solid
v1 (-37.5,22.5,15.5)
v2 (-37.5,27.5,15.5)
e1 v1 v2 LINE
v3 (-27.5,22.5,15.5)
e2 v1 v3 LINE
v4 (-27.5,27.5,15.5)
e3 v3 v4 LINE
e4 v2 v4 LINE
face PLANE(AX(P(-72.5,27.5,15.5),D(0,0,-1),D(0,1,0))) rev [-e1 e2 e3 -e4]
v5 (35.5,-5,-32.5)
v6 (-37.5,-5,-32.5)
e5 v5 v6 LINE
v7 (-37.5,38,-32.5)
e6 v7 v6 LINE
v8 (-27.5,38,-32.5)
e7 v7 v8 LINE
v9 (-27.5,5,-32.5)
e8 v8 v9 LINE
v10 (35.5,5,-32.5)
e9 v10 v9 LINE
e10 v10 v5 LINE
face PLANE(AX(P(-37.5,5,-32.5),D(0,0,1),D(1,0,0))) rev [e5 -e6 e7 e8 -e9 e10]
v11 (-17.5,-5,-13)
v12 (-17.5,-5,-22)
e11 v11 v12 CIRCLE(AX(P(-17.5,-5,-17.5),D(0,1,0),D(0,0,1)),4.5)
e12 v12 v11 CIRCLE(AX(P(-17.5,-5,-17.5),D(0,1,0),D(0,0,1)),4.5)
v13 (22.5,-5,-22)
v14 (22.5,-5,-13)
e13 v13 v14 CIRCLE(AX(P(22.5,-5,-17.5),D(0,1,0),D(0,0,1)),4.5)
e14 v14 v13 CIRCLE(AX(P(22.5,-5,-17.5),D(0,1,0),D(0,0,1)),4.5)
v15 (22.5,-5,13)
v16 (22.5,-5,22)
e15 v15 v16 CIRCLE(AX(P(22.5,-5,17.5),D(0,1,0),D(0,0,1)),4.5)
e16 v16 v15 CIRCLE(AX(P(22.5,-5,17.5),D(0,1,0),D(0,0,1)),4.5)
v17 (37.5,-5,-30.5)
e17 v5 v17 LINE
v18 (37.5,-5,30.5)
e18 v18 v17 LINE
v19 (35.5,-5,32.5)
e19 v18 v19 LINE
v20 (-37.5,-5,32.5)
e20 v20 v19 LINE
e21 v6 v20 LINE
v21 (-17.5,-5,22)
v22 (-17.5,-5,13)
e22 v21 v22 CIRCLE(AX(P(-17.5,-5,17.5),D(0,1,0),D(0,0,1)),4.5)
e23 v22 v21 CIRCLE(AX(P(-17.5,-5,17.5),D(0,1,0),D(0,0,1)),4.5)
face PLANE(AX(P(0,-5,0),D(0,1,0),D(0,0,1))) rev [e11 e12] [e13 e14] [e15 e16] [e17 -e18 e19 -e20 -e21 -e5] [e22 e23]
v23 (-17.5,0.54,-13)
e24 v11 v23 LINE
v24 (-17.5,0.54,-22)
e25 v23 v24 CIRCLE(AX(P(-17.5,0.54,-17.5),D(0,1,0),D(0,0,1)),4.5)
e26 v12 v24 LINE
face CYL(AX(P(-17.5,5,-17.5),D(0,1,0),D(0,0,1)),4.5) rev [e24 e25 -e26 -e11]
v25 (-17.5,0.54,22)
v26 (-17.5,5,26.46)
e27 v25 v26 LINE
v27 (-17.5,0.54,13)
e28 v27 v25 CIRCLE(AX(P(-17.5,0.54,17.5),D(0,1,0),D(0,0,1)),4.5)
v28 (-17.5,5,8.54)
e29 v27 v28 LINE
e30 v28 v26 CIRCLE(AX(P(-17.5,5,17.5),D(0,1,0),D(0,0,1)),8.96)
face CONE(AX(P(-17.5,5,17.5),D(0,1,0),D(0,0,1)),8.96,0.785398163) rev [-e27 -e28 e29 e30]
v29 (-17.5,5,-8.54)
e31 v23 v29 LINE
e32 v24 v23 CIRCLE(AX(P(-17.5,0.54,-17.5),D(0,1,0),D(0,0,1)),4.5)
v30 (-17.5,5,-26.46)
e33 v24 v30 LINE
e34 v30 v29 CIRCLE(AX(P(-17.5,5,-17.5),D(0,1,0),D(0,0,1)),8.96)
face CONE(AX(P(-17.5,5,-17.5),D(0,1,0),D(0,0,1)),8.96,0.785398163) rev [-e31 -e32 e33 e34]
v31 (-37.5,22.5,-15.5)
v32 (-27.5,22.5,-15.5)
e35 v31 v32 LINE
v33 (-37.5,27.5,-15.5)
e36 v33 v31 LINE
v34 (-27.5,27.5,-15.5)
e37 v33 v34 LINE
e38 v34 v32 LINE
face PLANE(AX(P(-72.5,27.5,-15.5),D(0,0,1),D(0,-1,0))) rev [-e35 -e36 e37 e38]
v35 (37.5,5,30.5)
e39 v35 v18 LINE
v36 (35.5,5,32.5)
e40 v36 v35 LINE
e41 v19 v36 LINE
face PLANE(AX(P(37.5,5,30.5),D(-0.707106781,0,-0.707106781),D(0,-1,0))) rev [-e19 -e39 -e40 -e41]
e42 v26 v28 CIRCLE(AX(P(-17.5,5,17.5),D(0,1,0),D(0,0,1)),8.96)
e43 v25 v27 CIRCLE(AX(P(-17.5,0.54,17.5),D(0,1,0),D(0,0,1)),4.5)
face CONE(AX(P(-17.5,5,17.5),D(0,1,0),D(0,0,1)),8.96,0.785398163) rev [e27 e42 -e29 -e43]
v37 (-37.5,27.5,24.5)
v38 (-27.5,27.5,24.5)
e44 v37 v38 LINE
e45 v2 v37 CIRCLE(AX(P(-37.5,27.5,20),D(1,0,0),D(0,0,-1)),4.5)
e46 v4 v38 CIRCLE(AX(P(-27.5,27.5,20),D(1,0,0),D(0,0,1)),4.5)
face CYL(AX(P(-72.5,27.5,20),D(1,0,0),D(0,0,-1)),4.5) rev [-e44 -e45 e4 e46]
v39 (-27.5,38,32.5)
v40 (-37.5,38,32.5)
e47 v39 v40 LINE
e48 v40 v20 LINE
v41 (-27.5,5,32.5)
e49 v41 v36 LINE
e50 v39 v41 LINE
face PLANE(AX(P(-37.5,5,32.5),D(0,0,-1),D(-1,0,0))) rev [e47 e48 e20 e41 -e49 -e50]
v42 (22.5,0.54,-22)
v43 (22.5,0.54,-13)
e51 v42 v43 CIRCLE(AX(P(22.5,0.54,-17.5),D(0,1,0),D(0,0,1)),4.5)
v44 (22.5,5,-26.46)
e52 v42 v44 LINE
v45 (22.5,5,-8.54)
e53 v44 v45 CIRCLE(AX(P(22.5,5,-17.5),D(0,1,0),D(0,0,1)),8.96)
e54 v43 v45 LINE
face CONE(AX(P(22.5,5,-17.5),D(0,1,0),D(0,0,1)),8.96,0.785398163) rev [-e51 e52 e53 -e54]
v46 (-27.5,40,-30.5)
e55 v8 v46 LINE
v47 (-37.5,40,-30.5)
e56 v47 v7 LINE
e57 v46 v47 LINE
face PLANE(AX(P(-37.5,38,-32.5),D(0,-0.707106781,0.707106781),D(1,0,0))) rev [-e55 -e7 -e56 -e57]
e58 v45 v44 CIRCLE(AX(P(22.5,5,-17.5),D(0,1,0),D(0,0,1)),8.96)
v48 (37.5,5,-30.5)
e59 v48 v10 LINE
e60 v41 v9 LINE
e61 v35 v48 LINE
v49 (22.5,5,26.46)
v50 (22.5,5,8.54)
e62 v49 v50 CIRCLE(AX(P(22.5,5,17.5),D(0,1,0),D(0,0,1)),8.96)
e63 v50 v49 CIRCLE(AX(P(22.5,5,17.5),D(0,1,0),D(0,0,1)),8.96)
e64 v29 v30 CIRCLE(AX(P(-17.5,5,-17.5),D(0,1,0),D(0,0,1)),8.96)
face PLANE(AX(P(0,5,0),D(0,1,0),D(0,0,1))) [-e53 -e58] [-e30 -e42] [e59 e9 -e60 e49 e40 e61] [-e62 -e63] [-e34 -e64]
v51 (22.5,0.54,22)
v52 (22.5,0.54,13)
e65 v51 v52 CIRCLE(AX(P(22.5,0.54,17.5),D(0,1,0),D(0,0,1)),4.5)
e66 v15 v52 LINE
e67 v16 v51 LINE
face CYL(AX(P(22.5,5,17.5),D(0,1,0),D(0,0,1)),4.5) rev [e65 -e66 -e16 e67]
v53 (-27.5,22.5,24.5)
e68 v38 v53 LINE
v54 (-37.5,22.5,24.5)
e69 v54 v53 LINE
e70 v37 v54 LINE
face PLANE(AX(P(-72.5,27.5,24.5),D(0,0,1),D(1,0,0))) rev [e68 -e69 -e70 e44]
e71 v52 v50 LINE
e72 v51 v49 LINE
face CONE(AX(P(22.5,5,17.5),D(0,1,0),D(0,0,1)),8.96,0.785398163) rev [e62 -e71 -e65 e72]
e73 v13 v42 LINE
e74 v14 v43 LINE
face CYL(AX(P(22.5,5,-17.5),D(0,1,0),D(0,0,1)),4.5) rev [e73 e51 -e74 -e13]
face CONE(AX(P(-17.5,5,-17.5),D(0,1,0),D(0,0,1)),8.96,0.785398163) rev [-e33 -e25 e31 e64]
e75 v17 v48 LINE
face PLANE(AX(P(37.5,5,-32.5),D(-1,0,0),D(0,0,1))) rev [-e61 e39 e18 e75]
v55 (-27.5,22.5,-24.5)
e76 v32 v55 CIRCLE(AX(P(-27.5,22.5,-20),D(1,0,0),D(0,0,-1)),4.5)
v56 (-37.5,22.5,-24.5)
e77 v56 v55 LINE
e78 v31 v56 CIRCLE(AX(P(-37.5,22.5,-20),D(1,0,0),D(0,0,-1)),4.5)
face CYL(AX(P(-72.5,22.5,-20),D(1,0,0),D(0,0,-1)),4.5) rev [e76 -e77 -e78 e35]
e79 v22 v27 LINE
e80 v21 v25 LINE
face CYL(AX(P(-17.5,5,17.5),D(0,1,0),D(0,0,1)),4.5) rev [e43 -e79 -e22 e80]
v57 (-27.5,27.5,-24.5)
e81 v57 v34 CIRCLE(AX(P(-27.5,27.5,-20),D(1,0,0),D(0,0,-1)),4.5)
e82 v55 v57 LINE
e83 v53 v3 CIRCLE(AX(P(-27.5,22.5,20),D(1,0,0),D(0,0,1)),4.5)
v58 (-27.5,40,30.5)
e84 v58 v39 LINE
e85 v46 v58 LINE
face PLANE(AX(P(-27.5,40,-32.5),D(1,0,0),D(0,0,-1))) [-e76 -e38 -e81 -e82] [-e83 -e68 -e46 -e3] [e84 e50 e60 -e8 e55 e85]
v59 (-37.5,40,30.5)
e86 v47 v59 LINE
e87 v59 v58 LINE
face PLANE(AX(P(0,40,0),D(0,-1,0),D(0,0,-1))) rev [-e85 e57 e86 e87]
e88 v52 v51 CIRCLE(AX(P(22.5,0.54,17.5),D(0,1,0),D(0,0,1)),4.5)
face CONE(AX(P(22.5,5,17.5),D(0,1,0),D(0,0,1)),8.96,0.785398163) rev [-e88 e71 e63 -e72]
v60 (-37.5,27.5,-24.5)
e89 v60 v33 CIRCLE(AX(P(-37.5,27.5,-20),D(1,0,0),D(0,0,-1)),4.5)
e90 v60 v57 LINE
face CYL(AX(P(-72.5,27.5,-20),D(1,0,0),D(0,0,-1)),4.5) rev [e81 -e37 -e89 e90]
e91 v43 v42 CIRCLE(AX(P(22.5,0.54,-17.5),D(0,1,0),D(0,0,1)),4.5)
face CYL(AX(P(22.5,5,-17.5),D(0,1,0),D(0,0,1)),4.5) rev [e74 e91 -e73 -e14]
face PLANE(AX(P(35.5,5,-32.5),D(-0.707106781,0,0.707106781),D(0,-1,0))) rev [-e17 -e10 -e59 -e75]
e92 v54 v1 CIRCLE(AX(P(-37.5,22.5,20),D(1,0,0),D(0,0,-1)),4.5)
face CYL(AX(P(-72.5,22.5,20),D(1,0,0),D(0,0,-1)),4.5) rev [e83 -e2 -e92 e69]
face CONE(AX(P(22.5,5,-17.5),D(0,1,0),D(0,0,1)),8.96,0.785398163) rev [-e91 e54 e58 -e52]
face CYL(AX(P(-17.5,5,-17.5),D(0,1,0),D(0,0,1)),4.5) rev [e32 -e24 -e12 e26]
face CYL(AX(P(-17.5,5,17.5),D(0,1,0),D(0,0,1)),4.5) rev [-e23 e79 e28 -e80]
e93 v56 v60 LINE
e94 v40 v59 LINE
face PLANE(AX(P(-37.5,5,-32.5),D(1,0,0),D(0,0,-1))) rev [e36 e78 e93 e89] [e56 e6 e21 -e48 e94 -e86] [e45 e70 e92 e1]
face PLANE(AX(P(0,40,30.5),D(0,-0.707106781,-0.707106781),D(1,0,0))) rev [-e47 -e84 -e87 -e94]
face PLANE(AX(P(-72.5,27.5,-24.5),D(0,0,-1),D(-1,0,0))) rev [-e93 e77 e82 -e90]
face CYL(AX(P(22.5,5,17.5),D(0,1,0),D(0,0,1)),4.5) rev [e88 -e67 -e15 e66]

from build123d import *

# Parameters (mm, degrees)
SKETCH_2_W                   = 75
SKETCH_2_H                   = 65
EXTRUDE_1_DEPTH              = 5
SKETCH_3_W                   = 10
SKETCH_3_H                   = 65
EXTRUDE_2_DEPTH              = 45
HOLE_WIZARD_M8_1_D           = 9
HOLE_WIZARD_M8_1_CSINK_D     = 17.92
HOLE_WIZARD_M8_1_CSINK_ANGLE = 90
CUT_EXTRUDE_1_DEPTH          = 45
CHAMFER_1_SIZE               = 2


with BuildPart() as part:
    # 草图2 → 凸台-拉伸1 (new, symmetric)
    with BuildSketch(Plane(origin=(0, 0, 0), x_dir=(1, 0, 0), z_dir=(0, 1, 0))):
        Rectangle(SKETCH_2_W, SKETCH_2_H)
    extrude(amount=EXTRUDE_1_DEPTH, both=True)

    # 草图3 → 凸台-拉伸2 (add)
    with BuildSketch(Plane.XZ.offset(5)):
        with Locations((-32.5, 0)):
            Rectangle(SKETCH_3_W, SKETCH_3_H)
    extrude(amount=-EXTRUDE_2_DEPTH)

    # M8 六角凹锥坑螺钉的锥形沉头孔1 (through all)
    with Locations(Plane(origin=(0, 5, 0), x_dir=(1, 0, 0), z_dir=(0, 1, 0))):
        with Locations((22.5, 17.5), (-17.5, 17.5), (-17.5, -17.5), (22.5, -17.5)):
            CounterSinkHole(HOLE_WIZARD_M8_1_D / 2, HOLE_WIZARD_M8_1_CSINK_D / 2, counter_sink_angle=HOLE_WIZARD_M8_1_CSINK_ANGLE)

    # 草图6 → 切除-拉伸1 (cut)
    with BuildSketch(Plane(origin=(-27.5, 0, 0), x_dir=(0, 0, -1), z_dir=(1, 0, 0))):
        with BuildLine():
            Line((24.5, 27.5), (24.5, 22.5))
            ThreePointArc((24.5, 22.5), (20, 18), (15.5, 22.5))
            Line((15.5, 22.5), (15.5, 27.5))
            ThreePointArc((15.5, 27.5), (20, 32), (24.5, 27.5))
        make_face()
        with BuildLine():
            Line((-24.5, 27.5), (-24.5, 22.5))
            ThreePointArc((-24.5, 22.5), (-20, 18), (-15.5, 22.5))
            Line((-15.5, 22.5), (-15.5, 27.5))
            ThreePointArc((-15.5, 27.5), (-20, 32), (-24.5, 27.5))
        make_face()
    extrude(amount=-CUT_EXTRUDE_1_DEPTH, mode=Mode.SUBTRACT)

    # 倒角1
    chamfer_1_edges = [part.edges().sort_by_distance(p)[0] for p in [
        (-32.5, 40, -32.5),
        (-32.5, 40, 32.5),
        (37.5, 0, 32.5),
        (37.5, 0, -32.5),
    ]]
    chamfer(chamfer_1_edges, length=CHAMFER_1_SIZE)


solid = part.part
